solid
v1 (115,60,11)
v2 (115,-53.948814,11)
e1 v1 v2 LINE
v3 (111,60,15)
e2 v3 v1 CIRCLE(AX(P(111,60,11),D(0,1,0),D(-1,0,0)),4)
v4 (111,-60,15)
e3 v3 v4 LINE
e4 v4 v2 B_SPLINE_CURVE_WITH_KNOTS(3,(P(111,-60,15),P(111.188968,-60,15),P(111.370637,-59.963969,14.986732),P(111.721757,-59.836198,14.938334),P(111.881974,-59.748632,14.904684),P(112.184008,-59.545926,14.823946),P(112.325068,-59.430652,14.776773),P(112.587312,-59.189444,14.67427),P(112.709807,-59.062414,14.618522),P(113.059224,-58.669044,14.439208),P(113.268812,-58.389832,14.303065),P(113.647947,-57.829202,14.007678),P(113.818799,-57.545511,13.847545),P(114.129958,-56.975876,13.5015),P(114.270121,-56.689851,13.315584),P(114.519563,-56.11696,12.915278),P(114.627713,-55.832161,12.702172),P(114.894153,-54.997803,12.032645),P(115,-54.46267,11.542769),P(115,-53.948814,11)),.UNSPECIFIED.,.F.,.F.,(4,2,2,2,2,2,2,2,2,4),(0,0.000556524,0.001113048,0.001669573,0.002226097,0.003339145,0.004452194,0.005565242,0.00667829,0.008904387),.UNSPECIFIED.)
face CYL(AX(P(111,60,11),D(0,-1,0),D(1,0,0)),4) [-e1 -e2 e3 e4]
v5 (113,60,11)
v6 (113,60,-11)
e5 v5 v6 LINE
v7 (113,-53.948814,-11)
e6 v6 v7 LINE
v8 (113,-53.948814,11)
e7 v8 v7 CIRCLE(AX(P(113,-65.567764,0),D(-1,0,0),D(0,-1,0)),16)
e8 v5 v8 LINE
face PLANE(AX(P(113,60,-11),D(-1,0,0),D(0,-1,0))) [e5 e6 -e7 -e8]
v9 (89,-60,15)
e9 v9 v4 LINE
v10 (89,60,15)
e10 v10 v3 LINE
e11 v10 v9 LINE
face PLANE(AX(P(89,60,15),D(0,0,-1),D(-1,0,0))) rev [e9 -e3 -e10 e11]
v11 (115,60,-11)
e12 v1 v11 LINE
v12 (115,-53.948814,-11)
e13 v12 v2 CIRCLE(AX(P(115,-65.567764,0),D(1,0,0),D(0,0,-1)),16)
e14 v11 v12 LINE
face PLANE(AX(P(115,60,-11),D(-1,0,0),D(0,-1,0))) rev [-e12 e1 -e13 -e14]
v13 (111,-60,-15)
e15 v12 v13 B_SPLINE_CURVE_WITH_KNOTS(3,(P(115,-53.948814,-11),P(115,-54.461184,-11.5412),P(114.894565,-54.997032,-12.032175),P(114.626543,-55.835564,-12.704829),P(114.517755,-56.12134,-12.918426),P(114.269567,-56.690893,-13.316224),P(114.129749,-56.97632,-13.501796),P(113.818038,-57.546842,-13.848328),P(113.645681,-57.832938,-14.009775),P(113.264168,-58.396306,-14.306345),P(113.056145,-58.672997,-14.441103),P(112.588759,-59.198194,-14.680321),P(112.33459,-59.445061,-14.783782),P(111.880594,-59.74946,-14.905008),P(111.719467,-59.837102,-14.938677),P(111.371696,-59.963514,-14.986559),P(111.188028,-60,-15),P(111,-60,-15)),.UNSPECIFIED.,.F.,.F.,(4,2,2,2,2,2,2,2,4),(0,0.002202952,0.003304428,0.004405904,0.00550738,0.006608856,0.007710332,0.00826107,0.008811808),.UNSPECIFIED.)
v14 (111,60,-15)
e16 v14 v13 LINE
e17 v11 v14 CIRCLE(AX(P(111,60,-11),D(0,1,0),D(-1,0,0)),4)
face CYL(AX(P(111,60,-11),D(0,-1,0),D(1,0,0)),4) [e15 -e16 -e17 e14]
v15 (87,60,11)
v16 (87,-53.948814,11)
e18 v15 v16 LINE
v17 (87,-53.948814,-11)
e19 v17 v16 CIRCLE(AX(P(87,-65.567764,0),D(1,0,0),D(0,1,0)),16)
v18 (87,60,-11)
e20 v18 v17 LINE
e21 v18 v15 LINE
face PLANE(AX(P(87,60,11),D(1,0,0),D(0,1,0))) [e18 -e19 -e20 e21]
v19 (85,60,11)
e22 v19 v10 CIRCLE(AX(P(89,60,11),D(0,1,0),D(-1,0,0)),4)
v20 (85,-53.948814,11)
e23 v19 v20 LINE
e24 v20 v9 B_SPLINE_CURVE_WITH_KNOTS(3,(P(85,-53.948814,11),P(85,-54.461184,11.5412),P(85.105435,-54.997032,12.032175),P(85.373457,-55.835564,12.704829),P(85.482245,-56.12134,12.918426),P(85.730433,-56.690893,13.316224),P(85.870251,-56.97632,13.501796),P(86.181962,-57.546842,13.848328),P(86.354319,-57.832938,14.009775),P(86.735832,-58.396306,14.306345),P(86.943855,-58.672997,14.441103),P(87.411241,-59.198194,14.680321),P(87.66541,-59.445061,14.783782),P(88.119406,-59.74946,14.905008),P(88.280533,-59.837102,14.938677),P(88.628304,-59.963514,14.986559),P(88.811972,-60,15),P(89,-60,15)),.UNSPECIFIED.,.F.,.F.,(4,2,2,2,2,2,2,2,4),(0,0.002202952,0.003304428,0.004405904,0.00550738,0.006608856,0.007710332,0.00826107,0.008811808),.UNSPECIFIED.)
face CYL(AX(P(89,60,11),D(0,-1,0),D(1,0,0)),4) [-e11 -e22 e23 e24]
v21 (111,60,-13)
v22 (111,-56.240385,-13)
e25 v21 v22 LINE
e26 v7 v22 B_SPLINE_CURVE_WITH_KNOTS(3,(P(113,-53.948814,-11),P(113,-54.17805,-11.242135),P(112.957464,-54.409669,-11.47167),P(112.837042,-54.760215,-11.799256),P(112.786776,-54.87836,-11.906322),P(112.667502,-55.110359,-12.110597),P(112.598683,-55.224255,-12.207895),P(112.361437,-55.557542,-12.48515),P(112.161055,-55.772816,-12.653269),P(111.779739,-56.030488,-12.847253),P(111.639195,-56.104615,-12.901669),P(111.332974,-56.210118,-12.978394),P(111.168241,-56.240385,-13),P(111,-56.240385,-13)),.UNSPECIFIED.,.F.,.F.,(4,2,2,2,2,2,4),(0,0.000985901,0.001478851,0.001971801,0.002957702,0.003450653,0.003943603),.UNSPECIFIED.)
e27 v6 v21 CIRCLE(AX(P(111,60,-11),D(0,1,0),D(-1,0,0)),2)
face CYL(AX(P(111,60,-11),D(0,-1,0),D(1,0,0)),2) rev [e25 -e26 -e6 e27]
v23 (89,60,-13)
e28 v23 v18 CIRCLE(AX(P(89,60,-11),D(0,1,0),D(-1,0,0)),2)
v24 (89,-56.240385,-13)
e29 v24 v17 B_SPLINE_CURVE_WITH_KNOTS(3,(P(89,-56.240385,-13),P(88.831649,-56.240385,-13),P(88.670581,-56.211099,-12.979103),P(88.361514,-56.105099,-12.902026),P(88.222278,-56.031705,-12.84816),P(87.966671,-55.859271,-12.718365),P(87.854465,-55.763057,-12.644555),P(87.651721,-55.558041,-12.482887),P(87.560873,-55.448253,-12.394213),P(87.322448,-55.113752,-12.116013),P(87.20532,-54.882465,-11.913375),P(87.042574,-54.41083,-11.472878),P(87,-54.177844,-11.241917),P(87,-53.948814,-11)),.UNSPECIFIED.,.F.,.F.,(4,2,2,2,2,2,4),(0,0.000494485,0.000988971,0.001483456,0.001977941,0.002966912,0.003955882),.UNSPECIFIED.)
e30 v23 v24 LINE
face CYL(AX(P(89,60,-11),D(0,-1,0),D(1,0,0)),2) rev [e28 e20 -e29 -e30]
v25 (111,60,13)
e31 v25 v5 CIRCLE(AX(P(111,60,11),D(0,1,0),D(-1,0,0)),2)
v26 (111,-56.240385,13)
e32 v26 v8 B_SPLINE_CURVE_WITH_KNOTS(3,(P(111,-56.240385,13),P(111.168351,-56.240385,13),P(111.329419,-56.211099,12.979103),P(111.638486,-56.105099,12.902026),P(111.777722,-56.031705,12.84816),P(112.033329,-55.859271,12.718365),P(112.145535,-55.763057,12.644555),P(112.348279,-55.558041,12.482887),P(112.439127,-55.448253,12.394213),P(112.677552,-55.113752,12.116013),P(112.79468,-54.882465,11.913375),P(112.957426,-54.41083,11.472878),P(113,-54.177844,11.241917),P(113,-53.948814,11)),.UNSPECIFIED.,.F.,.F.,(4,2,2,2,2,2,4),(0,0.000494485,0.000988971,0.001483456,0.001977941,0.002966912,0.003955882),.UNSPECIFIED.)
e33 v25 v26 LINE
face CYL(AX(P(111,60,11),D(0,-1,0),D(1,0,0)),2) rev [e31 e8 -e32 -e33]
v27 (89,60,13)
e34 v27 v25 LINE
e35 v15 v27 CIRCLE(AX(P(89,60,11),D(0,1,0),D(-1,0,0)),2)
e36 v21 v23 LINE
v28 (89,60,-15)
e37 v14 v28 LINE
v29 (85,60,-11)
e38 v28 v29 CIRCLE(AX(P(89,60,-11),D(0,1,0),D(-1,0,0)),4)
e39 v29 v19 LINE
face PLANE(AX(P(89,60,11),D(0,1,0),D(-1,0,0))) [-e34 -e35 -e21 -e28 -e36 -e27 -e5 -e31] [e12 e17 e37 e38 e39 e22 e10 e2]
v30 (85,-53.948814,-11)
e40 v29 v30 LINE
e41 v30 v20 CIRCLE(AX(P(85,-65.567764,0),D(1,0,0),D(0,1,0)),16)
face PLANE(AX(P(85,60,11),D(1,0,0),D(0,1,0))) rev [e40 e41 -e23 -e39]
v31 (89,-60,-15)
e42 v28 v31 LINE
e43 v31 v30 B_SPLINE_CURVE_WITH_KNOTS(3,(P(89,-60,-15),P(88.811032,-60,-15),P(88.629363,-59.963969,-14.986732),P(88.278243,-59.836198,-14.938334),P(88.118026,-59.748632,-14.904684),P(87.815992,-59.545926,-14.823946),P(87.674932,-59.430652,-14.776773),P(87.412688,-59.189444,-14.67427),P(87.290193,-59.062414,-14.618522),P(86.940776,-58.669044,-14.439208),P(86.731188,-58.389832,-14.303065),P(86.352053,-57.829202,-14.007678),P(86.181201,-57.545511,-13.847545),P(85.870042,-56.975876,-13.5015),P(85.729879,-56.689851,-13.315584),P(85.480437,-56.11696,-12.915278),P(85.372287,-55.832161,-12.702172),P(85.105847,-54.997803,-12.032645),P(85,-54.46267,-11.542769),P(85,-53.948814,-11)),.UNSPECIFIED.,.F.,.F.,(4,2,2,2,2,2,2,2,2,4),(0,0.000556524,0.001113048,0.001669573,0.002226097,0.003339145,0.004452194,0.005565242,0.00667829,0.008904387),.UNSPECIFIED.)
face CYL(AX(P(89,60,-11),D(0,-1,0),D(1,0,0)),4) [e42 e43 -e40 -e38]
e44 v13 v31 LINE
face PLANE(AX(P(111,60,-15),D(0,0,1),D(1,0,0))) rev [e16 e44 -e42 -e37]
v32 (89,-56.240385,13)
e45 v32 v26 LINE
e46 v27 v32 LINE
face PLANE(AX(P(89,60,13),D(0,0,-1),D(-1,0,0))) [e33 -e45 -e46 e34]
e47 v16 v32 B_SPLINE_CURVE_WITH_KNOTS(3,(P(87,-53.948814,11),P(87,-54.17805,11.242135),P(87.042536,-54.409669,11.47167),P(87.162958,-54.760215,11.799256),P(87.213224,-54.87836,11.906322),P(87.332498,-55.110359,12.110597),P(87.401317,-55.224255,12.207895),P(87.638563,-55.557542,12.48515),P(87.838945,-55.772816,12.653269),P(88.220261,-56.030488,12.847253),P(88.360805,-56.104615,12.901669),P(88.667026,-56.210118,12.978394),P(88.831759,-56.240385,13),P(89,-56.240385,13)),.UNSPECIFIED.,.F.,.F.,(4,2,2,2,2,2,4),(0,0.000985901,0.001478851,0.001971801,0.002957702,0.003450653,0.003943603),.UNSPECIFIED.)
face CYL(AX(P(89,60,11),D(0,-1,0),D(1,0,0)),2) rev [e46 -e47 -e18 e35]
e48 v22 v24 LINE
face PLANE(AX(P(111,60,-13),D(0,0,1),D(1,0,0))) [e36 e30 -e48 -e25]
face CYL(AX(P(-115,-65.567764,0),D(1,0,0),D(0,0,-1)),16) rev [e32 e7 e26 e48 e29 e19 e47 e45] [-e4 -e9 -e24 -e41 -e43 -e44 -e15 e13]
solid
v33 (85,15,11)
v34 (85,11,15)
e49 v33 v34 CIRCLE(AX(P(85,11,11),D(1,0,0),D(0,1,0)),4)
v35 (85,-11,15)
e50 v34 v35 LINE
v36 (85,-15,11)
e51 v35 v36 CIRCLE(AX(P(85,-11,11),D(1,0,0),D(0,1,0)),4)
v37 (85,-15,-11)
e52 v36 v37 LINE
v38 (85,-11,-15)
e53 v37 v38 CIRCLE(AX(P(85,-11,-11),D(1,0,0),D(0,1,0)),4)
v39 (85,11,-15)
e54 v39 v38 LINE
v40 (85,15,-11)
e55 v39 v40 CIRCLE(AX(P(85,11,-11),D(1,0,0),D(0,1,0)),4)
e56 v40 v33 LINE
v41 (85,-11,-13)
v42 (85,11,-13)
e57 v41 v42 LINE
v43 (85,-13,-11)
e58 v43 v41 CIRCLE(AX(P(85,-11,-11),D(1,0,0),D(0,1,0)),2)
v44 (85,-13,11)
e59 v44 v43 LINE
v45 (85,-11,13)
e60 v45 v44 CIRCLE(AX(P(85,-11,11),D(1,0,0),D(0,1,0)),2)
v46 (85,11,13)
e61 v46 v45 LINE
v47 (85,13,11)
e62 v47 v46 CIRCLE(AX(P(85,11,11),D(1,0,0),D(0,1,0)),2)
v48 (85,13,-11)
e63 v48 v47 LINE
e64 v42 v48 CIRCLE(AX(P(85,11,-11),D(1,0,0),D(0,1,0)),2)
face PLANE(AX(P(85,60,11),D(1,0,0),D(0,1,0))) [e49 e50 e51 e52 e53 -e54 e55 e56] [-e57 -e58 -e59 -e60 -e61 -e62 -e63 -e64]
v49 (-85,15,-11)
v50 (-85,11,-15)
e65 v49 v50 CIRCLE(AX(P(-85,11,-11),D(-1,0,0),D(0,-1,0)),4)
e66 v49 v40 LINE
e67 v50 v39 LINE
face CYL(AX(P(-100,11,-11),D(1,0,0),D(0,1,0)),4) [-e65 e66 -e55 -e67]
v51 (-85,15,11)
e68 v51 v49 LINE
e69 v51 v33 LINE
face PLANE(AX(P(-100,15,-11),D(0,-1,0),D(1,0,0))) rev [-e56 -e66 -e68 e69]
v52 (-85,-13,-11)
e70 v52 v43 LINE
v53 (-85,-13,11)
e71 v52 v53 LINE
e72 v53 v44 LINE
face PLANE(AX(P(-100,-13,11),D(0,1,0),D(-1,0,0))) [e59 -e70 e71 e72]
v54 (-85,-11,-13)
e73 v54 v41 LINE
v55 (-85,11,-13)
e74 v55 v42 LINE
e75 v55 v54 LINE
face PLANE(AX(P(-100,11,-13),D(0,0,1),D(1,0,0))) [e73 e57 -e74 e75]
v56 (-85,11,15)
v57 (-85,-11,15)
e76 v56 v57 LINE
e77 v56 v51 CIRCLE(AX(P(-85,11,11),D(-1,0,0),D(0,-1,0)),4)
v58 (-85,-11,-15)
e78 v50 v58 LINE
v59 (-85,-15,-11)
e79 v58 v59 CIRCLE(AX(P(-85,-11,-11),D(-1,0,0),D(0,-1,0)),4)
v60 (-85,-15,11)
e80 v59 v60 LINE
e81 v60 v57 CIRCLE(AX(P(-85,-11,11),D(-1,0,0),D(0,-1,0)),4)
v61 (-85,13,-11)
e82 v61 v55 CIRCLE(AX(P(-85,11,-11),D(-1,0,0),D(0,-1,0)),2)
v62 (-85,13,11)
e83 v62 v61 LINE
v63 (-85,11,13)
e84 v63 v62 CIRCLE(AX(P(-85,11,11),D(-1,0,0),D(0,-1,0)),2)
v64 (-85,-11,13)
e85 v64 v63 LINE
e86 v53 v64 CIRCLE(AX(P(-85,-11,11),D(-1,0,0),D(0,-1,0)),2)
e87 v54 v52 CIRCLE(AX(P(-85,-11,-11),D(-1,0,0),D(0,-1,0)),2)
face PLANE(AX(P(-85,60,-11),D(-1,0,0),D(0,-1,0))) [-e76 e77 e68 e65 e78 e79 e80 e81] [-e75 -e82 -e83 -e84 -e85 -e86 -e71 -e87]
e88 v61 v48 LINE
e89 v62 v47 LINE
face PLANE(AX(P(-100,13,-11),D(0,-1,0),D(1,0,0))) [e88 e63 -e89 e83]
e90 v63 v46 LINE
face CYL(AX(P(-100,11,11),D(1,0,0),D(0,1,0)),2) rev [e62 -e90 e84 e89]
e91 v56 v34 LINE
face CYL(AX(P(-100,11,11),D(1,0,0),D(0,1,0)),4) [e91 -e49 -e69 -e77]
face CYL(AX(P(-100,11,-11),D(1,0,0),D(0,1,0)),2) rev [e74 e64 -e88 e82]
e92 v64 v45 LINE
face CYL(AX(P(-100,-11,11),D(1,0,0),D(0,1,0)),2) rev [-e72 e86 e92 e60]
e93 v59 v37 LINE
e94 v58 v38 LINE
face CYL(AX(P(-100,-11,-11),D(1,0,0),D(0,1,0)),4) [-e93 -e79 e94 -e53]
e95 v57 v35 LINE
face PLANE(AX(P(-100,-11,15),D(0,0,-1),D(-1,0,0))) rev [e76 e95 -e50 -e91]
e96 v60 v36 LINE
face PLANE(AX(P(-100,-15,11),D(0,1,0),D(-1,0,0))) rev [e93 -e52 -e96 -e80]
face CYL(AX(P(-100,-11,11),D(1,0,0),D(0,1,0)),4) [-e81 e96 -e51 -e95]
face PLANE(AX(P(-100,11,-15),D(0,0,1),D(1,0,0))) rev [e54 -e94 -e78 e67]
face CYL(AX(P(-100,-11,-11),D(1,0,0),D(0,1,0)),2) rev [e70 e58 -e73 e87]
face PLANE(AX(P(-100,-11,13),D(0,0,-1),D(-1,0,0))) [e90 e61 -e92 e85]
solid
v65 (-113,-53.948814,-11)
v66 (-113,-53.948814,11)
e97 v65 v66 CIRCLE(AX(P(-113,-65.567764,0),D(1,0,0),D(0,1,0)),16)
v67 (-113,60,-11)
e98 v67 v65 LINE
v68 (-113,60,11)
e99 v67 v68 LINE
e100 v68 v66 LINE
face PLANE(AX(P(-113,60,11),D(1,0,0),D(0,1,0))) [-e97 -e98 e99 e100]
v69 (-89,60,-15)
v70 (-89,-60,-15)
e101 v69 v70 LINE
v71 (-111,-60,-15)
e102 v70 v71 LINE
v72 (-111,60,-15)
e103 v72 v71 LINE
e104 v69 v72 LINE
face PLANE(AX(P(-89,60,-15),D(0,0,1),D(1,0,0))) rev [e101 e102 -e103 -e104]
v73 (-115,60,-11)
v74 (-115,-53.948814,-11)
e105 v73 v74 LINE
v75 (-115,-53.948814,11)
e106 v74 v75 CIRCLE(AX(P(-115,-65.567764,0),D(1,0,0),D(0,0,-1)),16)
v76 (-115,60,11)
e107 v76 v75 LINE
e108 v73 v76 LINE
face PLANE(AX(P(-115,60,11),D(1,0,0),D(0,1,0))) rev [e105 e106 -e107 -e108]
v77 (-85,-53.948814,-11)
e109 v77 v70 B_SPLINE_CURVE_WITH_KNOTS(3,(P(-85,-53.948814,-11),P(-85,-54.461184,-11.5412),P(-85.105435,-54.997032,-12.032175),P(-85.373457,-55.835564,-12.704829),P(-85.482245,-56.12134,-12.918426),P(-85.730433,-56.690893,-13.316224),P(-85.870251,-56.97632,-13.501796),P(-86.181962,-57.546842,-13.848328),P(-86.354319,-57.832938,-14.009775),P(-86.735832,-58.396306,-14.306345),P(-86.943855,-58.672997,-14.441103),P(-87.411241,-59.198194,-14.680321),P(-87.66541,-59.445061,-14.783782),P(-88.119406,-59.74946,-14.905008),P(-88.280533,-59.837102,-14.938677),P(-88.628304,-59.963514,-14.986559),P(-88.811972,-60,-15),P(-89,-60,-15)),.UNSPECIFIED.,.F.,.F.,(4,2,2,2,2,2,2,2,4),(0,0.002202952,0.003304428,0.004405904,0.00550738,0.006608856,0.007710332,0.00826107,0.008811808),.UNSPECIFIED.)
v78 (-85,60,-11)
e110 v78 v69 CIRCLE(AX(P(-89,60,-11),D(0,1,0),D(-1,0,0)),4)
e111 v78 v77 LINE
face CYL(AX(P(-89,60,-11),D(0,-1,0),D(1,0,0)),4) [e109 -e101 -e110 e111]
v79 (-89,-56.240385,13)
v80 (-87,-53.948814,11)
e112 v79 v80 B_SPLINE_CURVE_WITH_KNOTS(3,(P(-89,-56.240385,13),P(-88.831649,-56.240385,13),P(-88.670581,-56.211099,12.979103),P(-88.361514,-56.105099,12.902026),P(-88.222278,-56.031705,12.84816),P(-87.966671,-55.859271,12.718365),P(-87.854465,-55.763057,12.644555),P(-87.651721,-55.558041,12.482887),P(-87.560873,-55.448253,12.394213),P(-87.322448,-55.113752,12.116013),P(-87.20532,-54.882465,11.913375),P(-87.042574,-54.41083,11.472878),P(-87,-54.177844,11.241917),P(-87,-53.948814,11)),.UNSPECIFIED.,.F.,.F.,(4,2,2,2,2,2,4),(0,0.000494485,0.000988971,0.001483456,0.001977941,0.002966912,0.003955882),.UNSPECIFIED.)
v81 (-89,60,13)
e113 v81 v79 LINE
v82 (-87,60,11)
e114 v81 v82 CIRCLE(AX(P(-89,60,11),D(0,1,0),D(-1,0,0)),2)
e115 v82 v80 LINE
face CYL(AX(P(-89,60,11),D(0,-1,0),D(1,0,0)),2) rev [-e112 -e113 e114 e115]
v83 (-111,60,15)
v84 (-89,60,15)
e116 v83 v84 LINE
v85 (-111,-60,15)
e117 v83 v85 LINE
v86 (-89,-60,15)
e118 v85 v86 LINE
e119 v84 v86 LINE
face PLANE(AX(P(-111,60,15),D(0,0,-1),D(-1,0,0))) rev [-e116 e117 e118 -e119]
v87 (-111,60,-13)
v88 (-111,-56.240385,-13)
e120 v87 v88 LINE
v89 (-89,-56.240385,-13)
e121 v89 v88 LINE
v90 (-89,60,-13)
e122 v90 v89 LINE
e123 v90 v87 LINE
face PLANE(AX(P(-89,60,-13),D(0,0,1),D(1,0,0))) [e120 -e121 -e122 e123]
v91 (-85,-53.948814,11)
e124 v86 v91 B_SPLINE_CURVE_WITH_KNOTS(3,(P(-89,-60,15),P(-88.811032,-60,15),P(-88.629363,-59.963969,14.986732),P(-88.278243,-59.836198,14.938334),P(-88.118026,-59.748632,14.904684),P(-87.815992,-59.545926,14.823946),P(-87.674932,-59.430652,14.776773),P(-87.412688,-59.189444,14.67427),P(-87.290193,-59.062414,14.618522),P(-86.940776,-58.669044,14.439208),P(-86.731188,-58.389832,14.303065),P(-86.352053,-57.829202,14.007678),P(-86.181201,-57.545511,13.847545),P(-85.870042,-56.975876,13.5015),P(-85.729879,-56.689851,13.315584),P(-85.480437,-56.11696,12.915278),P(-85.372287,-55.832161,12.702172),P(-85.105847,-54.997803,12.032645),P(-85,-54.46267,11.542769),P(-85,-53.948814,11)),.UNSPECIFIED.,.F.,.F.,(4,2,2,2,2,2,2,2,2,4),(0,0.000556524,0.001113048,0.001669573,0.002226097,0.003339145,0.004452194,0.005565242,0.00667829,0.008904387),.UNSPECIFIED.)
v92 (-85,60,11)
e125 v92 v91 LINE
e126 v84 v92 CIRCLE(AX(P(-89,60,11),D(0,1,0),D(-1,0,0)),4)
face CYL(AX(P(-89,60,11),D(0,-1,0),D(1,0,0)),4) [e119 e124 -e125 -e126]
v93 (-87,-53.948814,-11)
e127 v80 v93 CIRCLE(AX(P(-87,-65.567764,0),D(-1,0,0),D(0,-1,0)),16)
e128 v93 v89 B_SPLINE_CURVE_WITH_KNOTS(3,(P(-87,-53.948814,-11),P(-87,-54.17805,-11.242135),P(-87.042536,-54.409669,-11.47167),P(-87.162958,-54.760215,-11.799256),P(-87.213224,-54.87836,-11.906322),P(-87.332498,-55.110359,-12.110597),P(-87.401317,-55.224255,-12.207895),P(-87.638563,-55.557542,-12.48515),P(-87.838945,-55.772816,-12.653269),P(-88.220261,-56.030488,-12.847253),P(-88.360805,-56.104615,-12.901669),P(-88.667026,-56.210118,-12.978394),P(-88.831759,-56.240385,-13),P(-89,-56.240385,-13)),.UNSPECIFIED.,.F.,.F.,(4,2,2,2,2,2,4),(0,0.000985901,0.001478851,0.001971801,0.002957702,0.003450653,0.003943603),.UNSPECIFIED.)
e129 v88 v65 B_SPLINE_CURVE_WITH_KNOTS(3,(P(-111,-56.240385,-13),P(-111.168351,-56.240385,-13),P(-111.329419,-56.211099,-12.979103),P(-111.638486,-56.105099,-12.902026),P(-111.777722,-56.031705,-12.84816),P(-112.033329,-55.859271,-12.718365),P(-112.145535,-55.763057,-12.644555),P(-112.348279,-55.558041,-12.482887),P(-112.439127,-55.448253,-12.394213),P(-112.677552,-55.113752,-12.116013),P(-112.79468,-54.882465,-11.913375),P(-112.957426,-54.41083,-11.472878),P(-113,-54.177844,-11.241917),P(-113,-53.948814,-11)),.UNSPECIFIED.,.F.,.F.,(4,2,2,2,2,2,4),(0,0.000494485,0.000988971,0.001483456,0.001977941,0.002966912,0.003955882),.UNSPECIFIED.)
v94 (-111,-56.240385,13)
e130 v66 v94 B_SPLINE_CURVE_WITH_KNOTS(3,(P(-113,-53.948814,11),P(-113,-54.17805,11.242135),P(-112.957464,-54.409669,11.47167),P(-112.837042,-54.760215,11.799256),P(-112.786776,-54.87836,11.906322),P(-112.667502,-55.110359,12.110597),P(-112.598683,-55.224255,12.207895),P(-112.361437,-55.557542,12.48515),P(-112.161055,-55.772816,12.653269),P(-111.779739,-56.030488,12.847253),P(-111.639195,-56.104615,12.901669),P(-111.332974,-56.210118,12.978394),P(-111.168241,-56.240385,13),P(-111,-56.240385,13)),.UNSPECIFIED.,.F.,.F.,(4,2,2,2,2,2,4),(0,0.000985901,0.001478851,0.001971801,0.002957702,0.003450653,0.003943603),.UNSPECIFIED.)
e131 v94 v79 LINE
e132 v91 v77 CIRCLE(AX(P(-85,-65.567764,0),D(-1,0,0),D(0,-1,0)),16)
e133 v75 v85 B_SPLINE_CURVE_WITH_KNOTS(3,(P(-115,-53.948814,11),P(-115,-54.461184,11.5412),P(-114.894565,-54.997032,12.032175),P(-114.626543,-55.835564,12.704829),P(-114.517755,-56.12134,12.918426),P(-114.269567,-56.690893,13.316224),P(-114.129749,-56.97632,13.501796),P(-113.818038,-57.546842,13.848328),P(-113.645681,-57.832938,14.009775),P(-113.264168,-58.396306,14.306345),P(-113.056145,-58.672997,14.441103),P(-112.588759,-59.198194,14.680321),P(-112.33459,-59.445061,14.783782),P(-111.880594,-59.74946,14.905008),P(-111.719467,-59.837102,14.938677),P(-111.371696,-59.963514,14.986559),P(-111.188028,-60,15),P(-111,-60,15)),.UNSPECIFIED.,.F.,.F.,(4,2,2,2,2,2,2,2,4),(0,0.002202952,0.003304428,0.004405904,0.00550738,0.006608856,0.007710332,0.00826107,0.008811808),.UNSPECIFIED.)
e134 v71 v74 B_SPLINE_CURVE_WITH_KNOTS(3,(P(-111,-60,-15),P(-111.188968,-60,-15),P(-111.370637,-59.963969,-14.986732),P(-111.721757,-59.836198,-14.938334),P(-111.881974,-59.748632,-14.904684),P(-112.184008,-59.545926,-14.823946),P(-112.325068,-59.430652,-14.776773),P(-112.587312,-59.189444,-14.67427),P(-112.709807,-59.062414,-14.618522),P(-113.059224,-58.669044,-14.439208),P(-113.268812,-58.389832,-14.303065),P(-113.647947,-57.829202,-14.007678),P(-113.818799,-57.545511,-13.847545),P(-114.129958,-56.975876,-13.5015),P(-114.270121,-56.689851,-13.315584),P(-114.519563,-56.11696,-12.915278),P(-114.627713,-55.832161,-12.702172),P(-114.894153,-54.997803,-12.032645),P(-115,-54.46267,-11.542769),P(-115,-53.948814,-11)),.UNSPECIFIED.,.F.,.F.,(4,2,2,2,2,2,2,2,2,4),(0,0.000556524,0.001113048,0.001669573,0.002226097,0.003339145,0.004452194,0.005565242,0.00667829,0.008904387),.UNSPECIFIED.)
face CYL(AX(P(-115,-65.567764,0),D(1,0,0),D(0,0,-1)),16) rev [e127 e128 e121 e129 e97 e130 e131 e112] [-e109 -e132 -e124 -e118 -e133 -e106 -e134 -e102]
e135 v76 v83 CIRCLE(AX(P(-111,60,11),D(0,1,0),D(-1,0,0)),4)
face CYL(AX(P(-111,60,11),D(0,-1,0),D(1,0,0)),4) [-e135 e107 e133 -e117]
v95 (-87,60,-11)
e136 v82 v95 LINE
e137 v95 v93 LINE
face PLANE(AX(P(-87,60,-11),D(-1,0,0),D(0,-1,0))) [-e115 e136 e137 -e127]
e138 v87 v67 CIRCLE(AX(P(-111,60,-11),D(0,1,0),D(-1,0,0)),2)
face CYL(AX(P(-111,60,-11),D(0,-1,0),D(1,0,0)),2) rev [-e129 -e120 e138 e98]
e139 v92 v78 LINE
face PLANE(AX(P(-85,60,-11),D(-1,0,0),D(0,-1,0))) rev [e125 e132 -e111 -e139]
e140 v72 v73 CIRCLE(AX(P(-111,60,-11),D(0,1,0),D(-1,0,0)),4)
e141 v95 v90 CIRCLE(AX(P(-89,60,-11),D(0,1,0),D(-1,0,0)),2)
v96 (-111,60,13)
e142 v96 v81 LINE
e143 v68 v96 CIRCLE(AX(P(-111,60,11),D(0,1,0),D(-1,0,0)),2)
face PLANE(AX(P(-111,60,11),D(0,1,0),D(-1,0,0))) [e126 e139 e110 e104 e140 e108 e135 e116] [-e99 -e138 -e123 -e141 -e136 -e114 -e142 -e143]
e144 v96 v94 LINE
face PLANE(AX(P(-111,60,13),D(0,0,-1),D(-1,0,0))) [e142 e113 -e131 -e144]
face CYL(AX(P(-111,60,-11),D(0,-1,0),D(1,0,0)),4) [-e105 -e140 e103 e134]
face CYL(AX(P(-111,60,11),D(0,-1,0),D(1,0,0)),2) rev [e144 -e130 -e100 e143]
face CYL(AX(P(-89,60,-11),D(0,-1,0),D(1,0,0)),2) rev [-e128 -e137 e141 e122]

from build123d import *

# Parameters (mm, degrees)
GB_T_6728_2002_SQUARE_HOLLOW_SECTION_STE_DEPTH = 120
GB_T_6728_2002_SQUARE_HOLLOW_SECTION_2_DEPTH   = 120
GB_T_6728_2002_SQUARE_HOLLOW_SECTION_3_DEPTH   = 202
CUT_EXTRUDE1_DEPTH                             = 131.575648572
CUT_EXTRUDE1_DEPTH_BACK                        = 131.575648572
SKETCH3_R                                      = 16


with BuildPart() as part:
    # Sketch1 → Gb／t 6728—2002 Square hollow section steel 30×2-example.com(1) (new body)
    with BuildSketch(Plane(origin=(-100, -60, 0), x_dir=(-1, 0, 0), z_dir=(0, 1, 0))):
        with BuildLine():
            Line((-11, -15), (11, -15))
            ThreePointArc((11, -15), (13.828427125, -13.828427125), (15, -11))
            Line((15, -11), (15, 11))
            ThreePointArc((15, 11), (13.828427125, 13.828427125), (11, 15))
            Line((11, 15), (-11, 15))
            ThreePointArc((-11, 15), (-13.828427125, 13.828427125), (-15, 11))
            Line((-15, 11), (-15, -11))
            ThreePointArc((-15, -11), (-13.828427125, -13.828427125), (-11, -15))
        make_face()
        with BuildLine():
            Line((-11, -13), (11, -13))
            ThreePointArc((11, -13), (12.414213562, -12.414213562), (13, -11))
            Line((13, -11), (13, 11))
            ThreePointArc((13, 11), (12.414213562, 12.414213562), (11, 13))
            Line((11, 13), (-11, 13))
            ThreePointArc((-11, 13), (-12.414213562, 12.414213562), (-13, 11))
            Line((-13, 11), (-13, -11))
            ThreePointArc((-13, -11), (-12.414213562, -12.414213562), (-11, -13))
        make_face(mode=Mode.SUBTRACT)
    extrude(amount=GB_T_6728_2002_SQUARE_HOLLOW_SECTION_STE_DEPTH)


with BuildPart() as body_2:
    # Sketch1 on segment 2 (carried to segment 2) → Gb_t 6728_2002 Square hollow section 2 (new body)
    with BuildSketch(Plane(origin=(100, -60, 0), x_dir=(-1, 0, 0), z_dir=(0, 1, 0))):
        with BuildLine():
            Line((-11, -15), (11, -15))
            ThreePointArc((11, -15), (13.828427125, -13.828427125), (15, -11))
            Line((15, -11), (15, 11))
            ThreePointArc((15, 11), (13.828427125, 13.828427125), (11, 15))
            Line((11, 15), (-11, 15))
            ThreePointArc((-11, 15), (-13.828427125, 13.828427125), (-15, 11))
            Line((-15, 11), (-15, -11))
            ThreePointArc((-15, -11), (-13.828427125, -13.828427125), (-11, -15))
        make_face()
        with BuildLine():
            Line((-11, -13), (11, -13))
            ThreePointArc((11, -13), (12.414213562, -12.414213562), (13, -11))
            Line((13, -11), (13, 11))
            ThreePointArc((13, 11), (12.414213562, 12.414213562), (11, 13))
            Line((11, 13), (-11, 13))
            ThreePointArc((-11, 13), (-12.414213562, 12.414213562), (-13, 11))
            Line((-13, 11), (-13, -11))
            ThreePointArc((-13, -11), (-12.414213562, -12.414213562), (-11, -13))
        make_face(mode=Mode.SUBTRACT)
    extrude(amount=GB_T_6728_2002_SQUARE_HOLLOW_SECTION_2_DEPTH)


with BuildPart() as body_3:
    # Sketch1 on segment 3 (carried to segment 3) → Gb_t 6728_2002 Square hollow section 3 (new body)
    with BuildSketch(Plane(origin=(101, 0, 0), x_dir=(0, -1, 0), z_dir=(-1, 0, 0))):
        with BuildLine():
            Line((-11, -15), (11, -15))
            ThreePointArc((11, -15), (13.828427125, -13.828427125), (15, -11))
            Line((15, -11), (15, 11))
            ThreePointArc((15, 11), (13.828427125, 13.828427125), (11, 15))
            Line((11, 15), (-11, 15))
            ThreePointArc((-11, 15), (-13.828427125, 13.828427125), (-15, 11))
            Line((-15, 11), (-15, -11))
            ThreePointArc((-15, -11), (-13.828427125, -13.828427125), (-11, -15))
        make_face()
        with BuildLine():
            Line((-11, -13), (11, -13))
            ThreePointArc((11, -13), (12.414213562, -12.414213562), (13, -11))
            Line((13, -11), (13, 11))
            ThreePointArc((13, 11), (12.414213562, 12.414213562), (11, 13))
            Line((11, 13), (-11, 13))
            ThreePointArc((-11, 13), (-12.414213562, 12.414213562), (-13, 11))
            Line((-13, 11), (-13, -11))
            ThreePointArc((-13, -11), (-12.414213562, -12.414213562), (-11, -13))
        make_face(mode=Mode.SUBTRACT)
    extrude(amount=GB_T_6728_2002_SQUARE_HOLLOW_SECTION_3_DEPTH)

    # Gb_t 6728_2002 Square hollow section 3 e
    split(bisect_by=Plane(origin=(85, 0, 0), x_dir=(0, -1, 0), z_dir=(-1, 0, 0)), keep=Keep.TOP)

    # Gb_t 6728_2002 Square hollow section 4
    split(bisect_by=Plane.YZ.offset(-85), keep=Keep.TOP)


with BuildPart() as cut_extrude1_tool:
    # Sketch3 → Cut-Extrude1 (new, two sides: drawn at the far end of the back side and taken through both)
    with BuildSketch(Plane(origin=(0, 0, 0), x_dir=(0, 0, -1), z_dir=(1, 0, 0)).offset(-CUT_EXTRUDE1_DEPTH_BACK)):
        with Locations((0, -65.567764363)):
            Circle(SKETCH3_R)
    extrude(amount=CUT_EXTRUDE1_DEPTH + CUT_EXTRUDE1_DEPTH_BACK)


with BuildPart() as part_1:
    add(part.part)

    # Cut-Extrude1: cut by cut_extrude1_tool
    add(cut_extrude1_tool.part, mode=Mode.SUBTRACT)


with BuildPart() as body_2_1:
    add(body_2.part)

    # Cut-Extrude1: cut by cut_extrude1_tool
    add(cut_extrude1_tool.part, mode=Mode.SUBTRACT)


solid = Compound([body_3.part, part_1.part, body_2_1.part])
